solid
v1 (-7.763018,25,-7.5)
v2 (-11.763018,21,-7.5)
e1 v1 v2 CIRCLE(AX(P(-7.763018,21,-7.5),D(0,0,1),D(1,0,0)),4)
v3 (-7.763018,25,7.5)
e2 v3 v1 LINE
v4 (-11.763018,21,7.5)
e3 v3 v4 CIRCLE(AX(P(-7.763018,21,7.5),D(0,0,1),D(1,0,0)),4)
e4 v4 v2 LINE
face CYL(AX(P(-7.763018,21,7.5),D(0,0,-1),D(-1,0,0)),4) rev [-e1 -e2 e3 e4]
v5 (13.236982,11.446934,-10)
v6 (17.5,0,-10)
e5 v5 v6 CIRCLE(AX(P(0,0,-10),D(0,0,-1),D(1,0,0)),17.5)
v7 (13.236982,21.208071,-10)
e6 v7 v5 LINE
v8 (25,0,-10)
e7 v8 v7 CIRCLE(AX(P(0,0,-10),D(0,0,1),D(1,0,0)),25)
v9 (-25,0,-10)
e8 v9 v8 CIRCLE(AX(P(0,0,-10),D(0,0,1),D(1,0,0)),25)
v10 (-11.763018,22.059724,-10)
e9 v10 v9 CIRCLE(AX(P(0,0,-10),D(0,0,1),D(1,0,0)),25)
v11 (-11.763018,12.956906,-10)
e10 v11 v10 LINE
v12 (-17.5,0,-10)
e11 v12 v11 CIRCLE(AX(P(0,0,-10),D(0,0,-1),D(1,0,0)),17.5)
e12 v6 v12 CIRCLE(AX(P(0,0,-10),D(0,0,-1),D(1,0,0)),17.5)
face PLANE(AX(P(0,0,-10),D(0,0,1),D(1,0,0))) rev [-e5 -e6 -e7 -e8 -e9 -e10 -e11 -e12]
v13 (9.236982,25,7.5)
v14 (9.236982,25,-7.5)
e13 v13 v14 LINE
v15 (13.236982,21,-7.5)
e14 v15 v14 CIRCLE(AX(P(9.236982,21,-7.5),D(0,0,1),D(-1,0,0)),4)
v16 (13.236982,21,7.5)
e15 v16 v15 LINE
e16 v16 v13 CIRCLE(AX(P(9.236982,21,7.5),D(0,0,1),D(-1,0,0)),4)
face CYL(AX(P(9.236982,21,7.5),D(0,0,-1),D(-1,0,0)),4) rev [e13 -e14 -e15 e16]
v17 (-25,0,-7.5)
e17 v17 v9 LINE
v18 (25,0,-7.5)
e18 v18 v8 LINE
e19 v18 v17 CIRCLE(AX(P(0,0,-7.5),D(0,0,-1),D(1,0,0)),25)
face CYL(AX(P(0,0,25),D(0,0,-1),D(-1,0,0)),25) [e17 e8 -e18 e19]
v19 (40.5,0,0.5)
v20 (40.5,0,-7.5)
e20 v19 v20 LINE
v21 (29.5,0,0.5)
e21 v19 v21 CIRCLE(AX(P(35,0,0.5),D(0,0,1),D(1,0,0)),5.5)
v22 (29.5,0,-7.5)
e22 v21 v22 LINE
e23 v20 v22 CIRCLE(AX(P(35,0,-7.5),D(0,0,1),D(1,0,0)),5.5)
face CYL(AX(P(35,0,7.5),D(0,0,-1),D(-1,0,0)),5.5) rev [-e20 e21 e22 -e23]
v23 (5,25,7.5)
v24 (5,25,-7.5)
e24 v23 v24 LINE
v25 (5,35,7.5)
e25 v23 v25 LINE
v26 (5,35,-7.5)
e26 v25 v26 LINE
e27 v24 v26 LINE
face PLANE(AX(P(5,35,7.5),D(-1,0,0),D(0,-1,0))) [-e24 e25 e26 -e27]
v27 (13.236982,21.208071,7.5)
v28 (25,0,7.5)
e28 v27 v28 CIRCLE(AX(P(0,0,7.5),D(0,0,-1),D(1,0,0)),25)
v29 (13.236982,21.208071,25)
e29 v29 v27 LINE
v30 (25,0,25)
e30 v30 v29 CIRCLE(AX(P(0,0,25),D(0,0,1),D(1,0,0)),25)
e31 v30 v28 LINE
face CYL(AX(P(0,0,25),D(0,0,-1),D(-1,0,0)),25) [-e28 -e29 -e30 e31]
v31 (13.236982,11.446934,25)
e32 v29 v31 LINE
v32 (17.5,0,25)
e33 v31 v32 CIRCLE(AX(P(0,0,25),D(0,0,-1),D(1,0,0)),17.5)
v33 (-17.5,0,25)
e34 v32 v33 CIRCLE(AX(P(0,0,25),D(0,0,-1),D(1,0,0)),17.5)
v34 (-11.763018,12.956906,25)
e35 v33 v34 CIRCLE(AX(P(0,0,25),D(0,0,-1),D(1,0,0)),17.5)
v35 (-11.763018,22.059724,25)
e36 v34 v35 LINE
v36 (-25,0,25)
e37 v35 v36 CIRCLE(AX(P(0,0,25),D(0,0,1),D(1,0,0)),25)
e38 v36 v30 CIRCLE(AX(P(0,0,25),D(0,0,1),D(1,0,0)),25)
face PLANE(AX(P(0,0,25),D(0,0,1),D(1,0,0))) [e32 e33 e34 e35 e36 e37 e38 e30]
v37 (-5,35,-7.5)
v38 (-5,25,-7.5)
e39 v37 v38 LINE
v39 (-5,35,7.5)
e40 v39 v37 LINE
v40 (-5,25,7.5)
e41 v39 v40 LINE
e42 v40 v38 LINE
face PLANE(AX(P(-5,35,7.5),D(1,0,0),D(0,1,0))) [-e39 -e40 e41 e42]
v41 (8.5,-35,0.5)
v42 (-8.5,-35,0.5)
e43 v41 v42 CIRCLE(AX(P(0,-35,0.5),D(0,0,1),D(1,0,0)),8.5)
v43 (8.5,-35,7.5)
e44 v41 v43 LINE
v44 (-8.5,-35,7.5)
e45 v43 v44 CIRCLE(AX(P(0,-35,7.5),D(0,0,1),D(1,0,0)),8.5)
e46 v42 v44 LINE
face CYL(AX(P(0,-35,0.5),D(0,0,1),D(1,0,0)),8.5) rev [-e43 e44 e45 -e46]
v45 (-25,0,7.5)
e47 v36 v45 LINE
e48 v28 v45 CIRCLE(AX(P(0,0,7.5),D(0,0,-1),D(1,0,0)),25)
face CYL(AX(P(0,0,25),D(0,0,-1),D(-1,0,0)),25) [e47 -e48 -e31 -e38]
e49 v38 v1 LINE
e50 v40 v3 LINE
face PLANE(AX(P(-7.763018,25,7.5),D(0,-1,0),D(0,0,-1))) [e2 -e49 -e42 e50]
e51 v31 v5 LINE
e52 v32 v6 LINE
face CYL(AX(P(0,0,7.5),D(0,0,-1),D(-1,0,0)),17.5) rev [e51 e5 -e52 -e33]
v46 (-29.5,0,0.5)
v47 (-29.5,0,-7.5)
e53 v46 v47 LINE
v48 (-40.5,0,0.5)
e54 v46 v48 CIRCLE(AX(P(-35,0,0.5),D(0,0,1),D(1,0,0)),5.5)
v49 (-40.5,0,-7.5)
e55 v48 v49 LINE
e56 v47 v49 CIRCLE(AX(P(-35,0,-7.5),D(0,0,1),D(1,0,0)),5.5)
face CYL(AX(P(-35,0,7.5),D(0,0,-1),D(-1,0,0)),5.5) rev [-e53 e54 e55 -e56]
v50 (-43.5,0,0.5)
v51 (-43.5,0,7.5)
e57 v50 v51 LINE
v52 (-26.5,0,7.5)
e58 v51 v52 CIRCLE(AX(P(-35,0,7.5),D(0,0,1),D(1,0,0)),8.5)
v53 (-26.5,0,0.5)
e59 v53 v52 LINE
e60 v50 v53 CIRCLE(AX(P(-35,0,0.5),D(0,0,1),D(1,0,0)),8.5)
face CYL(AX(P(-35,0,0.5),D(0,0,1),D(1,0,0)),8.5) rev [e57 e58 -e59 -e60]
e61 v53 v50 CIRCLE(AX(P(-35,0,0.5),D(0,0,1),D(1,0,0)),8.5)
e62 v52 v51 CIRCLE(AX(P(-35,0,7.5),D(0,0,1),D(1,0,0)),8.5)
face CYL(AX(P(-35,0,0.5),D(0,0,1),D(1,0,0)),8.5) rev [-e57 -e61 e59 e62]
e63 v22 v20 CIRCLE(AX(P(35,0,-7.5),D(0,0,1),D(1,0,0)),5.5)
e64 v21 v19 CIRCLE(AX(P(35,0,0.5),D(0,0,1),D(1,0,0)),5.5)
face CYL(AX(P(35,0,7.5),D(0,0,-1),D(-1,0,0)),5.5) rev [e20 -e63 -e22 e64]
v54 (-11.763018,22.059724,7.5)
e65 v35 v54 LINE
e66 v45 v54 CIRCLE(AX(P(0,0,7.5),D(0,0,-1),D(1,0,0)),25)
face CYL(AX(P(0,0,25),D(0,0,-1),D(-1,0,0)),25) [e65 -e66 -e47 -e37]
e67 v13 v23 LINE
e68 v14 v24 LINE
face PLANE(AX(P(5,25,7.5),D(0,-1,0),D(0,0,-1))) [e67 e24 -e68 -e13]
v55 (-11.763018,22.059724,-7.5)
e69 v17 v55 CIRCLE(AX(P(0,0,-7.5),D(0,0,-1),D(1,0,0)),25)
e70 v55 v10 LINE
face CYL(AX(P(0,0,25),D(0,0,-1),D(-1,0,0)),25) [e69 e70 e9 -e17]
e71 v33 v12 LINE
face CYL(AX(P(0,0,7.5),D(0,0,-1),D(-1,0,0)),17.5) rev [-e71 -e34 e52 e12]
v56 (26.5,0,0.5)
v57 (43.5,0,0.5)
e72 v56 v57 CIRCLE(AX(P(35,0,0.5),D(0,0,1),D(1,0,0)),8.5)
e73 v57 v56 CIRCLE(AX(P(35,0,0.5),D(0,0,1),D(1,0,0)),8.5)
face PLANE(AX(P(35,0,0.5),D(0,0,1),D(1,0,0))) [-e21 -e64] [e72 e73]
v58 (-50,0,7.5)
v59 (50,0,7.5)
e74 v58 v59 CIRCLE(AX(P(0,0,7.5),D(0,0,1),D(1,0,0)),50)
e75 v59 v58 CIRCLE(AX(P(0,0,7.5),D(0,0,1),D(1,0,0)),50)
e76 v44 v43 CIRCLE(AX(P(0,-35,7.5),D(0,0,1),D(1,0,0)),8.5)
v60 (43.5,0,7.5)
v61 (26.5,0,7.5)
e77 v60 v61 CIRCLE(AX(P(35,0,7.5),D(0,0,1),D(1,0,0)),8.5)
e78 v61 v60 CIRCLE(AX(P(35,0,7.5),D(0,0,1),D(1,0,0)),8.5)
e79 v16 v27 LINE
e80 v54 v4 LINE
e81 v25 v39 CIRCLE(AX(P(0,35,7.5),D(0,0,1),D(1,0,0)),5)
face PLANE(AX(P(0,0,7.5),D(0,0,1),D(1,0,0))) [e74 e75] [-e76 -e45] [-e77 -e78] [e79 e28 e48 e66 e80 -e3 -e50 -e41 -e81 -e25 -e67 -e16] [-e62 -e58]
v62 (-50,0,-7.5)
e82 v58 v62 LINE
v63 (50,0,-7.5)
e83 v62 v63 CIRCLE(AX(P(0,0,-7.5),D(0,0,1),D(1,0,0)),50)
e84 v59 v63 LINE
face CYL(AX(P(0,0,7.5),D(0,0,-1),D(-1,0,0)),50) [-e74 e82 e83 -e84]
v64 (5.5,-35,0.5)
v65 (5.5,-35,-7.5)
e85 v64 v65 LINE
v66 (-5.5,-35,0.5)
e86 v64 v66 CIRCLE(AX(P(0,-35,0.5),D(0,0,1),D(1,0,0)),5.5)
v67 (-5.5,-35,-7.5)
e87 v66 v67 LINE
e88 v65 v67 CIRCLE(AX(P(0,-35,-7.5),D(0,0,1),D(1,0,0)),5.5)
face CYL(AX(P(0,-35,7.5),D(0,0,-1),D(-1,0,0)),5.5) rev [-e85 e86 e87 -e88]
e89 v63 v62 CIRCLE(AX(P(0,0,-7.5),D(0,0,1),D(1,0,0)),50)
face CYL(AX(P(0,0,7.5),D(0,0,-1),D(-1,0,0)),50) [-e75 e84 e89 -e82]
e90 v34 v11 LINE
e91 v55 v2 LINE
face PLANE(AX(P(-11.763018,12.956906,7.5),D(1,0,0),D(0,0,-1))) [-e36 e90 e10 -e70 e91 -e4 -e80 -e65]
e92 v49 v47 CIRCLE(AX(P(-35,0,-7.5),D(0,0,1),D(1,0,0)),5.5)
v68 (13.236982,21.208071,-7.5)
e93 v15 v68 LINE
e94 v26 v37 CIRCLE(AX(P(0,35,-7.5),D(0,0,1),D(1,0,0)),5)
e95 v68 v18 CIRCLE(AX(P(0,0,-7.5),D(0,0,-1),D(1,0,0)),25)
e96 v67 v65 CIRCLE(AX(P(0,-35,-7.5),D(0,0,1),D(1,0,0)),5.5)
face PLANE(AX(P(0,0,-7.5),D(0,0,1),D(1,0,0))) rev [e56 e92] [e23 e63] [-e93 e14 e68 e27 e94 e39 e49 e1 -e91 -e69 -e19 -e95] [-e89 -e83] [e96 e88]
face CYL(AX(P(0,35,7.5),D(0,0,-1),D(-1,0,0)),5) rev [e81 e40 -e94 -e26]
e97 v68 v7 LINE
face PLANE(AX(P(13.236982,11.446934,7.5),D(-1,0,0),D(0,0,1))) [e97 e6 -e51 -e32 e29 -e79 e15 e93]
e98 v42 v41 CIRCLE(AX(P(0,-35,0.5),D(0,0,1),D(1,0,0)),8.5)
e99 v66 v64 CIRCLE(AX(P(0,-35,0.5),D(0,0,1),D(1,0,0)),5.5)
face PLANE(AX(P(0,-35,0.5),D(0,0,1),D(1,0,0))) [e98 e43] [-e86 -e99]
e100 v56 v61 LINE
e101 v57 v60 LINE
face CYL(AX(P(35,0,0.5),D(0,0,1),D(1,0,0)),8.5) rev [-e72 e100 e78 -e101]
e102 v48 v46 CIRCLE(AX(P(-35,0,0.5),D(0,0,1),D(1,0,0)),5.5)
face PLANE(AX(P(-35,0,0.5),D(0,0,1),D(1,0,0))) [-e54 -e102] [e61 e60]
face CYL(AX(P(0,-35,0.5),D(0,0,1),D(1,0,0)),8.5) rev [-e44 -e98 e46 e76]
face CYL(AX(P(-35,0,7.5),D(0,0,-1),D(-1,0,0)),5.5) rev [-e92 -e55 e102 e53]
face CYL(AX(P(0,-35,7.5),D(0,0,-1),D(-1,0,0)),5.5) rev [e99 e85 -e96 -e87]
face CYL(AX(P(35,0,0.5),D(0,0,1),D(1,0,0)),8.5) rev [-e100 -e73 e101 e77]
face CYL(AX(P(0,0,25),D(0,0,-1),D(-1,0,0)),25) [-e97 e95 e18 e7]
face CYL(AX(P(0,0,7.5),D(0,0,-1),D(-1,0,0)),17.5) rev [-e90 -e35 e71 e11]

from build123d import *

# Parameters (mm, degrees)
FLANGE_PROFILE_SKETCH_R   = 50
FLANGE_PROFILE_SKETCH_R_2 = 5.5
FLANGE_100_DEPTH          = 7.5
HUB_50_DEPTH              = 17.5
HUB_SLOTS_SKETCH_R        = 8.5
HUB_SLOTS_4X_DEPTH        = 7


with BuildPart() as part:
    # Flange Profile Sketch → Flange Ø100 (new, symmetric)
    with BuildSketch(Plane.XY):
        Circle(FLANGE_PROFILE_SKETCH_R)
        with Locations((-35, 0)):
            Circle(FLANGE_PROFILE_SKETCH_R_2, mode=Mode.SUBTRACT)
        with Locations((35, 0)):
            Circle(FLANGE_PROFILE_SKETCH_R_2, mode=Mode.SUBTRACT)
        with Locations((0, -35)):
            Circle(FLANGE_PROFILE_SKETCH_R_2, mode=Mode.SUBTRACT)
        with BuildLine():
            Line((-11.763017547, 12.956906196), (-11.763017547, 21))
            ThreePointArc((-11.763017547, 21), (-10.591444672, 23.828427125), (-7.763017547, 25))
            Line((-7.763017547, 25), (-5, 25))
            Line((-5, 25), (-5, 35))
            ThreePointArc((-5, 35), (0, 40), (5, 35))
            Line((5, 35), (5, 25))
            Line((5, 25), (9.236982453, 25))
            ThreePointArc((9.236982453, 25), (12.065409578, 23.828427125), (13.236982453, 21))
            Line((13.236982453, 21), (13.236982453, 11.446933893))
            ThreePointArc((13.236982453, 11.446933893), (-1.055057925, -17.468166841), (-11.763017547, 12.956906196))
        make_face(mode=Mode.SUBTRACT)
    extrude(amount=FLANGE_100_DEPTH, both=True)

    # Hub Profile Sketch → Hub Ø50 (add, symmetric)
    with BuildSketch(Plane.XY.offset(7.5)):
        with BuildLine():
            Line((-11.763017547, 12.956906196), (-11.763017547, 22.059723892))
            ThreePointArc((-11.763017547, 22.059723892), (-0.851158679, -24.985506377), (13.236982453, 21.208071472))
            Line((13.236982453, 21.208071472), (13.236982453, 11.446933893))
            ThreePointArc((13.236982453, 11.446933893), (-1.055057925, -17.468166841), (-11.763017547, 12.956906196))
        make_face()
    extrude(amount=HUB_50_DEPTH, both=True)

    # Hub Slots Sketch → Hub Slots 4x (cut)
    with BuildSketch(Plane.XY.offset(7.5)):
        with Locations((-35, 0)):
            Circle(HUB_SLOTS_SKETCH_R)
        with Locations((35, 0)):
            Circle(HUB_SLOTS_SKETCH_R)
        with Locations((0, -35)):
            Circle(HUB_SLOTS_SKETCH_R)
    extrude(amount=-HUB_SLOTS_4X_DEPTH, mode=Mode.SUBTRACT)


solid = part.part
